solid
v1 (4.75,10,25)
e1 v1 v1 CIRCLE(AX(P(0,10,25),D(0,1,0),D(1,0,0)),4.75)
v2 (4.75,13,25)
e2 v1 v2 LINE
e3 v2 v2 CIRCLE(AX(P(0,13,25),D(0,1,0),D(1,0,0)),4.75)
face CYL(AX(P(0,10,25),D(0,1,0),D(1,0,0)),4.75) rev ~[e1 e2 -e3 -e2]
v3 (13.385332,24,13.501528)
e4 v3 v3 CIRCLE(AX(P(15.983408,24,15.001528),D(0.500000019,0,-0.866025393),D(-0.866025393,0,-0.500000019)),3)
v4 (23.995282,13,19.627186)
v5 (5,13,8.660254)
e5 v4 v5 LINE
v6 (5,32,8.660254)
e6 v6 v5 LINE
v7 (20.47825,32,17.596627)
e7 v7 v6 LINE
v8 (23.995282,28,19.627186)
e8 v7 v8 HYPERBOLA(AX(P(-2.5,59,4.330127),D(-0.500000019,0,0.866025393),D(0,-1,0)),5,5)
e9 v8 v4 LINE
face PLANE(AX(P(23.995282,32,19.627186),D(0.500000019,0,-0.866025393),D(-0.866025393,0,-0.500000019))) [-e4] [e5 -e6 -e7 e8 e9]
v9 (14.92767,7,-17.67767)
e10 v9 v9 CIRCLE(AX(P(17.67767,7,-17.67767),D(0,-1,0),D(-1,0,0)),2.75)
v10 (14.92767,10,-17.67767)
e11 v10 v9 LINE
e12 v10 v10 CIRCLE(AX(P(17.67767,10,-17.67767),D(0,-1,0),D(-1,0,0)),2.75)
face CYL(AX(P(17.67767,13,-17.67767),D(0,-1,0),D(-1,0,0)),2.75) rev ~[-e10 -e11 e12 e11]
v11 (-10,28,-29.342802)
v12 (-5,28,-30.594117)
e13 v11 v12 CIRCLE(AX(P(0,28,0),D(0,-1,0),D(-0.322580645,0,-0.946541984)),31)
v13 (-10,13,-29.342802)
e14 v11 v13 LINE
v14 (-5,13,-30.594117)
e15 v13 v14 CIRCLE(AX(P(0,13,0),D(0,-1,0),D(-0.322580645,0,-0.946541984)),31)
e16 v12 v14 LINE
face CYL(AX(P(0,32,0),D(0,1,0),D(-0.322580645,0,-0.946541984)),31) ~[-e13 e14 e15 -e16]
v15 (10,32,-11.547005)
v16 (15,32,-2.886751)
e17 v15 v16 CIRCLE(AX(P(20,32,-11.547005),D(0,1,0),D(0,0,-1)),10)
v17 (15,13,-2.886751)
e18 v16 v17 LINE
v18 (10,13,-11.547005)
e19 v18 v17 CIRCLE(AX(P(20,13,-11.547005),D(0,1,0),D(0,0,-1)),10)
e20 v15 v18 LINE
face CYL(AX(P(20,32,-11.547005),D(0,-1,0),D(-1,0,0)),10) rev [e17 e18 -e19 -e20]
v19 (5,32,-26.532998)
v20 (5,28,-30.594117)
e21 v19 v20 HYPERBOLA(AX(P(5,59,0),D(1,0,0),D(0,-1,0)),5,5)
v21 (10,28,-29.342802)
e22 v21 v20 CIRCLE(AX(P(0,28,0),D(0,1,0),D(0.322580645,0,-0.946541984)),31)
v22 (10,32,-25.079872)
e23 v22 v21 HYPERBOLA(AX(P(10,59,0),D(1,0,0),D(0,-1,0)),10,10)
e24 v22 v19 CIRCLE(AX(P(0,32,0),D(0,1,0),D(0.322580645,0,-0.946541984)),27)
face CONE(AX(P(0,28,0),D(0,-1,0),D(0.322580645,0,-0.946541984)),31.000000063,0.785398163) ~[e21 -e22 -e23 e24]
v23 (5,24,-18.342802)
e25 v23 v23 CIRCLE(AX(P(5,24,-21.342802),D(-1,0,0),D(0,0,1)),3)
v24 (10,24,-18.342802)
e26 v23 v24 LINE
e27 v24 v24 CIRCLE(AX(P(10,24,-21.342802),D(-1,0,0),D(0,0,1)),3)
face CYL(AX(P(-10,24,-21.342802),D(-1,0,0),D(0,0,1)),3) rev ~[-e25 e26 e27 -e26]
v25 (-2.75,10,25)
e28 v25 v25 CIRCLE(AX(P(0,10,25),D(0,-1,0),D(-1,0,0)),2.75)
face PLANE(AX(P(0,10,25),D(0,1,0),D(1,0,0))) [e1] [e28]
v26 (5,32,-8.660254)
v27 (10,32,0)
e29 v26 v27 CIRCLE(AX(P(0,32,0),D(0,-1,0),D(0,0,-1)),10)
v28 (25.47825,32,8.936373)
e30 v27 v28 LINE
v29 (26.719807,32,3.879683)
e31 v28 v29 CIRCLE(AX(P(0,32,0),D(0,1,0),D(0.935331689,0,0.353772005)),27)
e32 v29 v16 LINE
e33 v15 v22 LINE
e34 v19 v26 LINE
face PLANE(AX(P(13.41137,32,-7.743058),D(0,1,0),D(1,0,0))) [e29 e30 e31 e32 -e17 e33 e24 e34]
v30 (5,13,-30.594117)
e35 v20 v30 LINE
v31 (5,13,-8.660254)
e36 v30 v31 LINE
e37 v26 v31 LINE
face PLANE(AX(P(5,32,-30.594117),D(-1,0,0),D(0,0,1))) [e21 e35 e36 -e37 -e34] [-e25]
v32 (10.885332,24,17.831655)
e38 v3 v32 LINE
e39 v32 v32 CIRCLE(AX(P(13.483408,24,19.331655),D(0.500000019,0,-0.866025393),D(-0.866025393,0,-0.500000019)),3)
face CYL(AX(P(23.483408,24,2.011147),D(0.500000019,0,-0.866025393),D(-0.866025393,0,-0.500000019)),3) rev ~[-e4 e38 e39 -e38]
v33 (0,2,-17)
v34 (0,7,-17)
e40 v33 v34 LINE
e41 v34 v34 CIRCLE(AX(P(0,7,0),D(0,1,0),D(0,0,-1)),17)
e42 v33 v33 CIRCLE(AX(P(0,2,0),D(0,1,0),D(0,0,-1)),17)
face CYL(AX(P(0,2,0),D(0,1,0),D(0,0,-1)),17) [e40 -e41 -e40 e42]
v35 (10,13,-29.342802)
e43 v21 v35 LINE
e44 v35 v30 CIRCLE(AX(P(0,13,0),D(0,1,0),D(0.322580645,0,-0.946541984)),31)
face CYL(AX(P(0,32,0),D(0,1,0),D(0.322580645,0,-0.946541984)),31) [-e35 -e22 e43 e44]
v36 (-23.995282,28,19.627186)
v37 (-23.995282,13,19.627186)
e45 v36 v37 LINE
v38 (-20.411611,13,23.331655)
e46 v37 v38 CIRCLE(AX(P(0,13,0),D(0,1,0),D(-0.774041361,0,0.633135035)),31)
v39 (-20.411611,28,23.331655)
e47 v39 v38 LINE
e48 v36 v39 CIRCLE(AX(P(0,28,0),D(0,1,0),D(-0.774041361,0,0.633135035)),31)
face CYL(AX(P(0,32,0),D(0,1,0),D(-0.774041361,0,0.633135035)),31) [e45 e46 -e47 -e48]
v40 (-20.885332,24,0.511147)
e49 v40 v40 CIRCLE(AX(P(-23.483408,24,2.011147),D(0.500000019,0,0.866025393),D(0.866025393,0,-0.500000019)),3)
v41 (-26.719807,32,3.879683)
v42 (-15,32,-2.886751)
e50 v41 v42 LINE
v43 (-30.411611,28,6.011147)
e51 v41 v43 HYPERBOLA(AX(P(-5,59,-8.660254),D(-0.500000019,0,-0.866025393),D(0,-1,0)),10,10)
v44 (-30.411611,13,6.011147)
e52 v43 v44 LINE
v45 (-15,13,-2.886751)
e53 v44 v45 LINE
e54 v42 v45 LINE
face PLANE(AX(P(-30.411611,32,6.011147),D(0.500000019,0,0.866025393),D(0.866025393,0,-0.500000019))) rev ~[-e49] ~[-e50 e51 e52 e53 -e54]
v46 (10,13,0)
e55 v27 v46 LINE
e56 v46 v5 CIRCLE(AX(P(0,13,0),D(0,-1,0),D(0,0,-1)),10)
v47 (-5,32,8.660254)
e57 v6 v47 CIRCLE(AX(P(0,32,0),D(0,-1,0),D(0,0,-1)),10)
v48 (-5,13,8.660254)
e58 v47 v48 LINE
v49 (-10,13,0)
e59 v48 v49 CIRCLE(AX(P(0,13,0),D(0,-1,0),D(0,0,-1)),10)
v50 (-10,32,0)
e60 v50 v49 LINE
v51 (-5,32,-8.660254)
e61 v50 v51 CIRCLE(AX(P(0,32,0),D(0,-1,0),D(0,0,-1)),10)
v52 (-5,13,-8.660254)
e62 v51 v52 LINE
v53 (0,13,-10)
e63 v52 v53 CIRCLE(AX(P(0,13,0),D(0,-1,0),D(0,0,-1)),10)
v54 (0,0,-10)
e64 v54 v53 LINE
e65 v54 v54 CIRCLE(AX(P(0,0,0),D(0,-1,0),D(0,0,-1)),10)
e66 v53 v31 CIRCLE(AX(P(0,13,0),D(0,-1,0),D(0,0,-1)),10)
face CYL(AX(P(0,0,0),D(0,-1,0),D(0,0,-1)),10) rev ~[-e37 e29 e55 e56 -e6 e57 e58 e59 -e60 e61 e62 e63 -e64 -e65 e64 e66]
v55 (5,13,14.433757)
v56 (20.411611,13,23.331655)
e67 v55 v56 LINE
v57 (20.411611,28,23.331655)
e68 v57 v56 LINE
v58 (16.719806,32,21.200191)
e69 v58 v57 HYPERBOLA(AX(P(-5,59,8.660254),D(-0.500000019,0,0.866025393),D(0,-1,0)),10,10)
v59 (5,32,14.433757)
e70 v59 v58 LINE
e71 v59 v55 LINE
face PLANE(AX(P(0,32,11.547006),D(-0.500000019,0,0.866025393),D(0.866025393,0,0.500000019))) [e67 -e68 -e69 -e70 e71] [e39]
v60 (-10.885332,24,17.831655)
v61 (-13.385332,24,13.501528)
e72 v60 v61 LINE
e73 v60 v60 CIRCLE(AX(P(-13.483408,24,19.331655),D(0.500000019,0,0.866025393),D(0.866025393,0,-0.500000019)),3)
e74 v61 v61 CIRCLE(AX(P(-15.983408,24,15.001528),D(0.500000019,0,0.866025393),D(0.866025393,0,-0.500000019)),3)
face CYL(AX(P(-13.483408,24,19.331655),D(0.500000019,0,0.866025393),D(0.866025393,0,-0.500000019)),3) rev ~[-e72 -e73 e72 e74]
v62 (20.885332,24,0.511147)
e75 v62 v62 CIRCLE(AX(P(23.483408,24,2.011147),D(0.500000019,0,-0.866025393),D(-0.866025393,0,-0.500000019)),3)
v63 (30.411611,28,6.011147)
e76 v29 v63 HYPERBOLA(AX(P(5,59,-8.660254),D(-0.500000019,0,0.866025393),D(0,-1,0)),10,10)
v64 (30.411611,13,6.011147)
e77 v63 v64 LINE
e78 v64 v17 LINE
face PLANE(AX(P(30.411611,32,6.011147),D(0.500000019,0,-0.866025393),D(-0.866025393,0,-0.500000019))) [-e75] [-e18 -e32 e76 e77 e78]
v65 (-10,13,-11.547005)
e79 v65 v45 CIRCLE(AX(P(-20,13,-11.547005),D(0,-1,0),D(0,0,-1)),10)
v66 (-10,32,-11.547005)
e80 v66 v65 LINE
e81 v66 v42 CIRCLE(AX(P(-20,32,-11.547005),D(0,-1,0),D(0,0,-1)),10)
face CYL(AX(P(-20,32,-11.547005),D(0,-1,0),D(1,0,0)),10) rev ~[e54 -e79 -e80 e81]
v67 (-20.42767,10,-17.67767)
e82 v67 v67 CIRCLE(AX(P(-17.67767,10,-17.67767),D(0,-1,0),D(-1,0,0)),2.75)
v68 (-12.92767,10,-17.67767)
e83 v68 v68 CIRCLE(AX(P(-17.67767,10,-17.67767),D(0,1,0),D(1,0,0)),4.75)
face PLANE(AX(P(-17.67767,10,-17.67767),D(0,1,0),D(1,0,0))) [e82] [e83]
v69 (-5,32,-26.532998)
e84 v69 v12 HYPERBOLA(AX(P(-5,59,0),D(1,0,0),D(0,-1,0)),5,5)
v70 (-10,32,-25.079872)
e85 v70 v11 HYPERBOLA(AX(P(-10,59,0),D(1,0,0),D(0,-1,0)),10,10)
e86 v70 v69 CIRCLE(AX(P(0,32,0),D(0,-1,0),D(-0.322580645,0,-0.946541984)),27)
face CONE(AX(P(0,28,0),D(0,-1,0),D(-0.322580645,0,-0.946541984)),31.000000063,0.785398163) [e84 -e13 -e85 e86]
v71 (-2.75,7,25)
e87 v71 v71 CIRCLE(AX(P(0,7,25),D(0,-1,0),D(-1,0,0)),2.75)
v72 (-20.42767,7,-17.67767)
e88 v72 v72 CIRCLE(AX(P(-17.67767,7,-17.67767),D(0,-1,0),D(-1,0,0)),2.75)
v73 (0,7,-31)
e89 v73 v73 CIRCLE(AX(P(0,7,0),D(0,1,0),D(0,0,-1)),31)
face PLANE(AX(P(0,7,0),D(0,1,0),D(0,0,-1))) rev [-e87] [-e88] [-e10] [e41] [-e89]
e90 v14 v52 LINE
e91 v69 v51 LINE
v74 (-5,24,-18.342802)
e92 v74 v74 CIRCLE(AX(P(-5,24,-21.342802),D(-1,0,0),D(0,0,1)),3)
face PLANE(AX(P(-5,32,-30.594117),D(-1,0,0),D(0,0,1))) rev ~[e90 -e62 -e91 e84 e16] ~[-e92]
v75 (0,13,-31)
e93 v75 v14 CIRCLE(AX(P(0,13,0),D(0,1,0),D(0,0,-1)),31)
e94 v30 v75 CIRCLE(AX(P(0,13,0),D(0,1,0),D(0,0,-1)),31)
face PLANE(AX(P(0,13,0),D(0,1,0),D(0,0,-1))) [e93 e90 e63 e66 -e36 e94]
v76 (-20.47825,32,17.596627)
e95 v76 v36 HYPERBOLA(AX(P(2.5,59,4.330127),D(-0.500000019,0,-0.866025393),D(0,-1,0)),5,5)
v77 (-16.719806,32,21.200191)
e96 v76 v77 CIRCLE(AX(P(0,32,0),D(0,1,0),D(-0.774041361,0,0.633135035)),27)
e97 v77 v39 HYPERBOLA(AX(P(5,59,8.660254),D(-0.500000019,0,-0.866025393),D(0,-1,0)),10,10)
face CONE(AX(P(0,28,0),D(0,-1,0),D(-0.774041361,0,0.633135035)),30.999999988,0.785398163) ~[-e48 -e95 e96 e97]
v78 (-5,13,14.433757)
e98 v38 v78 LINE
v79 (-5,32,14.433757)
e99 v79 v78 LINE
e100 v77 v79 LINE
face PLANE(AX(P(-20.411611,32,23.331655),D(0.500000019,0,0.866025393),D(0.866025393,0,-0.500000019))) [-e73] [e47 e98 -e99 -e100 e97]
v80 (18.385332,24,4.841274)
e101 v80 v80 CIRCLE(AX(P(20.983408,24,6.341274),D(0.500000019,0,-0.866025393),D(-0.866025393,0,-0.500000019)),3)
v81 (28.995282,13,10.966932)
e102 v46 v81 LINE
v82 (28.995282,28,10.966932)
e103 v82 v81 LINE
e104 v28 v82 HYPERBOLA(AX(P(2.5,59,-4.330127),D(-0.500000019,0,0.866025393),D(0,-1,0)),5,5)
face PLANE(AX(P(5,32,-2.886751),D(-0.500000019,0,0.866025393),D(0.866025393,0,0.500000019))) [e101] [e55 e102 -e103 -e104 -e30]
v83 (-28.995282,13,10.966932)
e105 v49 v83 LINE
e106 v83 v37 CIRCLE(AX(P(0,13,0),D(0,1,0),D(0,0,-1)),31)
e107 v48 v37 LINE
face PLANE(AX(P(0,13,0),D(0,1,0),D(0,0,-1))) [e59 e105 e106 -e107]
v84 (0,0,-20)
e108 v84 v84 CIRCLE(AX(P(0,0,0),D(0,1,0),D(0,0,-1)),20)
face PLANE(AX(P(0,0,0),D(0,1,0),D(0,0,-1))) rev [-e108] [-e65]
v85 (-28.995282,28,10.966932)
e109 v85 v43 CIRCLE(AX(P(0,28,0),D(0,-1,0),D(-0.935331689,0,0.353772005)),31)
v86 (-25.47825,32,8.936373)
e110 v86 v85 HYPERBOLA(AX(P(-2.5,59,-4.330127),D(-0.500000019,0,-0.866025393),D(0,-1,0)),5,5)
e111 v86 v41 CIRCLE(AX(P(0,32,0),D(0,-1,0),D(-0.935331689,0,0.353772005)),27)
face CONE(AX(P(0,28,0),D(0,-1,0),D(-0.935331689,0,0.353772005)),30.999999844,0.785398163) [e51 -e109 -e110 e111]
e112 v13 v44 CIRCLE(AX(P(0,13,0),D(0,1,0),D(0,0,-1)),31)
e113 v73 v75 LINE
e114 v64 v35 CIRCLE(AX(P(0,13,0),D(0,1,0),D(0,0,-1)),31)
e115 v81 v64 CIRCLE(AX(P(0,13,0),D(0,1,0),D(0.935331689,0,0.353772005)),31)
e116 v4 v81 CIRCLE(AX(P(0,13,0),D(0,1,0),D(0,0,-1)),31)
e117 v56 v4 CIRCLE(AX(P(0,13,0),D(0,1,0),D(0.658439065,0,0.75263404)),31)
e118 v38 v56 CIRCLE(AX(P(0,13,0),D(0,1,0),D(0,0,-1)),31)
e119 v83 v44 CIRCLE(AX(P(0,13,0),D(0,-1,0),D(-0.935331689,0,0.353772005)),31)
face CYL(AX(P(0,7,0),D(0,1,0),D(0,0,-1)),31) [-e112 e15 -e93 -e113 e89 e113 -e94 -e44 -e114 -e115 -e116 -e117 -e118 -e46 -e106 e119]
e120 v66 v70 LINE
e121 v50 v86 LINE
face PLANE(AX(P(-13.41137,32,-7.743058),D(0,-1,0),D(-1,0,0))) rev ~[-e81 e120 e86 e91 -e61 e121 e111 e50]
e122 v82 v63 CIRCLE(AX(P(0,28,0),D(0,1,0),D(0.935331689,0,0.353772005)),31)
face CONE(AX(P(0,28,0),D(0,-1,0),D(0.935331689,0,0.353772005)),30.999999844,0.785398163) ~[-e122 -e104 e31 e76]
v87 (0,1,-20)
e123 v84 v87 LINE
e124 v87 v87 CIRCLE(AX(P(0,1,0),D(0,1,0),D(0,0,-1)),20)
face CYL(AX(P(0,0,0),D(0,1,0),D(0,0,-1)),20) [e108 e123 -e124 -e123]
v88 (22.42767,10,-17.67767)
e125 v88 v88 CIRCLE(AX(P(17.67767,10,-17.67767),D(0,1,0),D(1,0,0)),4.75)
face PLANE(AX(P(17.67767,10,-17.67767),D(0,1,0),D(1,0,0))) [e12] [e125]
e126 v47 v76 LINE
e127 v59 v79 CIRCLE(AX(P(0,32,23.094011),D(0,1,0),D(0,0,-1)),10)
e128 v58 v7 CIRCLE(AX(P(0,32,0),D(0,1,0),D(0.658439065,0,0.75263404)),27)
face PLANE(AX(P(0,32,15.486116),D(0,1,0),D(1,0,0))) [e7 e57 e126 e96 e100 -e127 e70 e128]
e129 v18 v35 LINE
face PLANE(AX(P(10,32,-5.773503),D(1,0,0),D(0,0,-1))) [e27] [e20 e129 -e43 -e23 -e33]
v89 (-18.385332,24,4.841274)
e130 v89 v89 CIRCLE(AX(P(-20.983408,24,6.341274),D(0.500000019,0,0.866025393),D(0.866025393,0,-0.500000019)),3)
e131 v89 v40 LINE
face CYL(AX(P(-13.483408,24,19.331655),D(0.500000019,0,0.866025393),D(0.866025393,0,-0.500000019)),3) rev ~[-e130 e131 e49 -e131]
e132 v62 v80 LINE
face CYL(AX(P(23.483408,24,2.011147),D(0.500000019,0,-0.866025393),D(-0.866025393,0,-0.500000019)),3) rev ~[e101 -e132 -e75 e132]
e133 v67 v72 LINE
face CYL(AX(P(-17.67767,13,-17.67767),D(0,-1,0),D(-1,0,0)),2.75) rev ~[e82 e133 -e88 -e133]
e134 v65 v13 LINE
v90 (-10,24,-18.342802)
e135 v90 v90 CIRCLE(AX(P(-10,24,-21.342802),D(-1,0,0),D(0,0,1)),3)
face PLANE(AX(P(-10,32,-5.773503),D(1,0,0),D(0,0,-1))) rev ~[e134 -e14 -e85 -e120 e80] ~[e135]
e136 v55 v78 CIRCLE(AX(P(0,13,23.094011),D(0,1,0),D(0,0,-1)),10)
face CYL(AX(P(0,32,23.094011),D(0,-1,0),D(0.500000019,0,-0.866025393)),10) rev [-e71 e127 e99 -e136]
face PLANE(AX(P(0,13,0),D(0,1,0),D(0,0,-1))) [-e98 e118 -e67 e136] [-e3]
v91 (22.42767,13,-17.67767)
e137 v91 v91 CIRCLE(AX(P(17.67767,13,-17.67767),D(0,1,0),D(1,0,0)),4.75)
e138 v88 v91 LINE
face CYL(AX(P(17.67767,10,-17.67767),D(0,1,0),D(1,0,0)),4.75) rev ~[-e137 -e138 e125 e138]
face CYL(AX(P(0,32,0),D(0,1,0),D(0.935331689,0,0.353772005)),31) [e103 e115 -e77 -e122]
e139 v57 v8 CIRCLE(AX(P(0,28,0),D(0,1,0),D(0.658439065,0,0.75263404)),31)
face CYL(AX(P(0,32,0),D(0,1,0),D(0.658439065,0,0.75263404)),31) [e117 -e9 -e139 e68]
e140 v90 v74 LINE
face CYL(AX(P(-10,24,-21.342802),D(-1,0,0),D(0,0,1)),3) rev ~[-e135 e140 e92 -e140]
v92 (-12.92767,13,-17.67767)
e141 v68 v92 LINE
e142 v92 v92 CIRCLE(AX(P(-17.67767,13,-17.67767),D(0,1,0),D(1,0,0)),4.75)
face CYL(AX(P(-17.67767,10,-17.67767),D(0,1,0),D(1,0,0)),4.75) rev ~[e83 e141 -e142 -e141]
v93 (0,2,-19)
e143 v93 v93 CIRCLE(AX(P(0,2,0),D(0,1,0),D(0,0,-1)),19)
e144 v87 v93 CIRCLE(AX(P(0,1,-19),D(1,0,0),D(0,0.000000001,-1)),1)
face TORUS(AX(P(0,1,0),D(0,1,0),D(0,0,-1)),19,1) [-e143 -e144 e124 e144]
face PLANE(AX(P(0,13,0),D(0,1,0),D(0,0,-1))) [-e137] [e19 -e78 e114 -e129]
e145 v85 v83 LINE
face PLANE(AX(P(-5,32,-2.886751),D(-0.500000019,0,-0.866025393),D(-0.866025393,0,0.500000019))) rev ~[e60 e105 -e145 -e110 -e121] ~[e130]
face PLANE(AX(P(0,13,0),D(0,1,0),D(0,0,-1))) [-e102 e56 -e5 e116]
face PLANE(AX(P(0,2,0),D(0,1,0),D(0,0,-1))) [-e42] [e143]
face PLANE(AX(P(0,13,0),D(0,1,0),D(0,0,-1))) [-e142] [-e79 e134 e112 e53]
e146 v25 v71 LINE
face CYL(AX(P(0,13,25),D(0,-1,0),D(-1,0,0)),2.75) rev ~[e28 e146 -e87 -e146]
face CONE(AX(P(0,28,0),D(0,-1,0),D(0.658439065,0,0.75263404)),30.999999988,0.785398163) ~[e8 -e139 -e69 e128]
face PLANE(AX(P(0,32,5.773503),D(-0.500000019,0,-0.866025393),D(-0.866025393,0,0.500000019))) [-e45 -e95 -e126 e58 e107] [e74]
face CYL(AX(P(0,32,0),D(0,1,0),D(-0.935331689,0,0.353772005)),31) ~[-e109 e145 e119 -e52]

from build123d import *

# Parameters (mm, degrees)
THREE_START                       = 19
THREE_ARMS_DEPTH                  = 19
CENTRE_BORE_SKETCH_R              = 10
CENTRE_BORE_DEPTH                 = 79
ARM_FILLETS_R10_A_R               = 10
ARM_FILLETS_R10_B_R               = 10
ARM_HOLE_1_SKETCH_R               = 3
ARM_HOLE_1_DEPTH                  = 79
ARM_HOLE_2_SKETCH_R               = 3
ARM_HOLE_2_DEPTH                  = 79
ARM_HOLE_3_SKETCH_R               = 3
ARM_HOLE_3_DEPTH                  = 79
ARM_CHAMFER_4MM_SIZE              = 4
BASE_C_BORE_HOLES_5_5_D           = 5.5
BASE_C_BORE_HOLES_5_5_DEPTH       = 9
BASE_C_BORE_HOLES_5_5_CBORE_D     = 9.5
BASE_C_BORE_HOLES_5_5_CBORE_DEPTH = 3


with BuildPart() as part:
    # Base Hub Profile → Base Hub (revolve)
    with BuildSketch(Plane.XY, mode=Mode.PRIVATE) as base_hub_sk:
        with BuildLine():
            Line((0, 0), (-20, 0))
            Line((-20, 0), (-20, 1))
            ThreePointArc((-20, 1), (-19.707106781, 1.707106781), (-19, 2))
            Line((-19, 2), (-17, 2))
            Line((-17, 2), (-17, 7))
            Line((-17, 7), (-31, 7))
            Line((-31, 7), (-31, 13))
            Line((-31, 13), (0, 13))
            Line((0, 13), (0, 0))
        make_face()
    revolve(base_hub_sk.sketch.rotate(Axis((0, 0, 0), (0, 1, 0)), 270), axis=Axis((0, 0, 0), (0, 1, 0)))

    # Arms Profile → Three Arms (add)
    with BuildSketch(Plane(origin=(0, 13, 0), x_dir=(1, 0, 0), z_dir=(0, 1, 0)).offset(THREE_START)):
        with BuildLine():
            Line((-5, 30.594117082), (-5, 2.886751274))
            Line((-5, 2.886751274), (-28.995282363, -10.966932145))
            ThreePointArc((-28.995282363, -10.966932145), (-29.806621866, -8.518526455), (-30.41161139, -6.011147367))
            Line((-30.41161139, -6.011147367), (-10, 5.773502549))
            Line((-10, 5.773502549), (-10, 29.342801502))
            ThreePointArc((-10, 29.342801502), (-7.526051267, 30.072554802), (-5, 30.594117082))
        make_face()
        with BuildLine():
            Line((5, 30.594117082), (5, 2.886751274))
            Line((5, 2.886751274), (28.995282363, -10.966932145))
            ThreePointArc((28.995282363, -10.966932145), (29.806621866, -8.518526455), (30.41161139, -6.011147367))
            Line((30.41161139, -6.011147367), (10, 5.773502549))
            Line((10, 5.773502549), (10, 29.342801502))
            ThreePointArc((10, 29.342801502), (7.526051267, 30.072554802), (5, 30.594117082))
        make_face()
        with BuildLine():
            Line((23.995282177, -19.627186076), (0, -5.773502764))
            Line((0, -5.773502764), (-23.995282177, -19.627186076))
            ThreePointArc((-23.995282177, -19.627186076), (-22.280570319, -21.554029467), (-20.411611017, -23.331655228))
            Line((-20.411611017, -23.331655228), (0, -11.547005527))
            Line((0, -11.547005527), (20.411611017, -23.331655228))
            ThreePointArc((20.411611017, -23.331655228), (22.280570319, -21.554029467), (23.995282177, -19.627186076))
        make_face()
    extrude(amount=-THREE_ARMS_DEPTH)

    # Centre Bore Sketch → Centre Bore (cut)
    with BuildSketch(Plane.XZ):
        with Locations(Location((0, 0, 0), (0, 0, 270))):
            Circle(CENTRE_BORE_SKETCH_R)
    extrude(amount=-CENTRE_BORE_DEPTH, mode=Mode.SUBTRACT)

    # Arm Fillets R10 A
    arm_fillets_r10_a_edges = [part.edges().sort_by_distance(p)[0] for p in [
        (-10, 22.5, -5.773502549),
    ]]
    fillet(arm_fillets_r10_a_edges, radius=ARM_FILLETS_R10_A_R)

    # Arm Fillets R10 B
    arm_fillets_r10_b_edges = [part.edges().sort_by_distance(p)[0] for p in [
        (0, 22.5, 11.547005527),
        (10, 22.5, -5.773502549),
    ]]
    fillet(arm_fillets_r10_b_edges, radius=ARM_FILLETS_R10_B_R)

    # Arm Hole 1 Sketch → Arm Hole 1 (cut)
    with BuildSketch(Plane(origin=(5.000000186, 0, 8.66025393), x_dir=(0.8660253930337038, 0, -0.5000000186208186), z_dir=(0.5000000186208186, 0, 0.8660253930337038))):
        with Locations((-21.342801502, 24)):
            Circle(ARM_HOLE_1_SKETCH_R)
    extrude(amount=-ARM_HOLE_1_DEPTH, mode=Mode.SUBTRACT)

    # Arm Hole 2 Sketch → Arm Hole 2 (cut)
    with BuildSketch(Plane.ZY.offset(10)):
        with Locations((-21.342801502, 24)):
            Circle(ARM_HOLE_2_SKETCH_R)
    extrude(amount=-ARM_HOLE_2_DEPTH, mode=Mode.SUBTRACT)

    # Arm Hole 3 Sketch → Arm Hole 3 (cut)
    with BuildSketch(Plane(origin=(5.000000186, 0, -8.66025393), x_dir=(-0.866025393033704, 0, -0.5000000186208184), z_dir=(0.5000000186208183, 0, -0.8660253930337038))):
        with Locations((-21.342801502, 24)):
            Circle(ARM_HOLE_3_SKETCH_R)
    extrude(amount=-ARM_HOLE_3_DEPTH, mode=Mode.SUBTRACT)

    # Arm Chamfer 4mm
    arm_chamfer_4mm_edges = [part.edges().sort_by_distance(p)[0] for p in [
        (-7.526051267, 32, -30.072554802),
        (-29.806621866, 32, 8.518526455),
        (-22.280570319, 32, 21.554029467),
        (22.280570319, 32, 21.554029467),
        (7.526051267, 32, -30.072554802),
        (29.806621866, 32, 8.518526455),
    ]]
    chamfer(arm_chamfer_4mm_edges, length=ARM_CHAMFER_4MM_SIZE)

    # Base C-Bore Holes Ø5.5
    with Locations(Plane(origin=(0, 13, 0), x_dir=(1, 0, 0), z_dir=(0, 1, 0))):
        with Locations((-17.67766953, 17.67766953), (0, -25), (17.67766953, 17.67766953)):
            CounterBoreHole(BASE_C_BORE_HOLES_5_5_D / 2, BASE_C_BORE_HOLES_5_5_CBORE_D / 2, BASE_C_BORE_HOLES_5_5_CBORE_DEPTH, depth=BASE_C_BORE_HOLES_5_5_DEPTH)


solid = part.part
